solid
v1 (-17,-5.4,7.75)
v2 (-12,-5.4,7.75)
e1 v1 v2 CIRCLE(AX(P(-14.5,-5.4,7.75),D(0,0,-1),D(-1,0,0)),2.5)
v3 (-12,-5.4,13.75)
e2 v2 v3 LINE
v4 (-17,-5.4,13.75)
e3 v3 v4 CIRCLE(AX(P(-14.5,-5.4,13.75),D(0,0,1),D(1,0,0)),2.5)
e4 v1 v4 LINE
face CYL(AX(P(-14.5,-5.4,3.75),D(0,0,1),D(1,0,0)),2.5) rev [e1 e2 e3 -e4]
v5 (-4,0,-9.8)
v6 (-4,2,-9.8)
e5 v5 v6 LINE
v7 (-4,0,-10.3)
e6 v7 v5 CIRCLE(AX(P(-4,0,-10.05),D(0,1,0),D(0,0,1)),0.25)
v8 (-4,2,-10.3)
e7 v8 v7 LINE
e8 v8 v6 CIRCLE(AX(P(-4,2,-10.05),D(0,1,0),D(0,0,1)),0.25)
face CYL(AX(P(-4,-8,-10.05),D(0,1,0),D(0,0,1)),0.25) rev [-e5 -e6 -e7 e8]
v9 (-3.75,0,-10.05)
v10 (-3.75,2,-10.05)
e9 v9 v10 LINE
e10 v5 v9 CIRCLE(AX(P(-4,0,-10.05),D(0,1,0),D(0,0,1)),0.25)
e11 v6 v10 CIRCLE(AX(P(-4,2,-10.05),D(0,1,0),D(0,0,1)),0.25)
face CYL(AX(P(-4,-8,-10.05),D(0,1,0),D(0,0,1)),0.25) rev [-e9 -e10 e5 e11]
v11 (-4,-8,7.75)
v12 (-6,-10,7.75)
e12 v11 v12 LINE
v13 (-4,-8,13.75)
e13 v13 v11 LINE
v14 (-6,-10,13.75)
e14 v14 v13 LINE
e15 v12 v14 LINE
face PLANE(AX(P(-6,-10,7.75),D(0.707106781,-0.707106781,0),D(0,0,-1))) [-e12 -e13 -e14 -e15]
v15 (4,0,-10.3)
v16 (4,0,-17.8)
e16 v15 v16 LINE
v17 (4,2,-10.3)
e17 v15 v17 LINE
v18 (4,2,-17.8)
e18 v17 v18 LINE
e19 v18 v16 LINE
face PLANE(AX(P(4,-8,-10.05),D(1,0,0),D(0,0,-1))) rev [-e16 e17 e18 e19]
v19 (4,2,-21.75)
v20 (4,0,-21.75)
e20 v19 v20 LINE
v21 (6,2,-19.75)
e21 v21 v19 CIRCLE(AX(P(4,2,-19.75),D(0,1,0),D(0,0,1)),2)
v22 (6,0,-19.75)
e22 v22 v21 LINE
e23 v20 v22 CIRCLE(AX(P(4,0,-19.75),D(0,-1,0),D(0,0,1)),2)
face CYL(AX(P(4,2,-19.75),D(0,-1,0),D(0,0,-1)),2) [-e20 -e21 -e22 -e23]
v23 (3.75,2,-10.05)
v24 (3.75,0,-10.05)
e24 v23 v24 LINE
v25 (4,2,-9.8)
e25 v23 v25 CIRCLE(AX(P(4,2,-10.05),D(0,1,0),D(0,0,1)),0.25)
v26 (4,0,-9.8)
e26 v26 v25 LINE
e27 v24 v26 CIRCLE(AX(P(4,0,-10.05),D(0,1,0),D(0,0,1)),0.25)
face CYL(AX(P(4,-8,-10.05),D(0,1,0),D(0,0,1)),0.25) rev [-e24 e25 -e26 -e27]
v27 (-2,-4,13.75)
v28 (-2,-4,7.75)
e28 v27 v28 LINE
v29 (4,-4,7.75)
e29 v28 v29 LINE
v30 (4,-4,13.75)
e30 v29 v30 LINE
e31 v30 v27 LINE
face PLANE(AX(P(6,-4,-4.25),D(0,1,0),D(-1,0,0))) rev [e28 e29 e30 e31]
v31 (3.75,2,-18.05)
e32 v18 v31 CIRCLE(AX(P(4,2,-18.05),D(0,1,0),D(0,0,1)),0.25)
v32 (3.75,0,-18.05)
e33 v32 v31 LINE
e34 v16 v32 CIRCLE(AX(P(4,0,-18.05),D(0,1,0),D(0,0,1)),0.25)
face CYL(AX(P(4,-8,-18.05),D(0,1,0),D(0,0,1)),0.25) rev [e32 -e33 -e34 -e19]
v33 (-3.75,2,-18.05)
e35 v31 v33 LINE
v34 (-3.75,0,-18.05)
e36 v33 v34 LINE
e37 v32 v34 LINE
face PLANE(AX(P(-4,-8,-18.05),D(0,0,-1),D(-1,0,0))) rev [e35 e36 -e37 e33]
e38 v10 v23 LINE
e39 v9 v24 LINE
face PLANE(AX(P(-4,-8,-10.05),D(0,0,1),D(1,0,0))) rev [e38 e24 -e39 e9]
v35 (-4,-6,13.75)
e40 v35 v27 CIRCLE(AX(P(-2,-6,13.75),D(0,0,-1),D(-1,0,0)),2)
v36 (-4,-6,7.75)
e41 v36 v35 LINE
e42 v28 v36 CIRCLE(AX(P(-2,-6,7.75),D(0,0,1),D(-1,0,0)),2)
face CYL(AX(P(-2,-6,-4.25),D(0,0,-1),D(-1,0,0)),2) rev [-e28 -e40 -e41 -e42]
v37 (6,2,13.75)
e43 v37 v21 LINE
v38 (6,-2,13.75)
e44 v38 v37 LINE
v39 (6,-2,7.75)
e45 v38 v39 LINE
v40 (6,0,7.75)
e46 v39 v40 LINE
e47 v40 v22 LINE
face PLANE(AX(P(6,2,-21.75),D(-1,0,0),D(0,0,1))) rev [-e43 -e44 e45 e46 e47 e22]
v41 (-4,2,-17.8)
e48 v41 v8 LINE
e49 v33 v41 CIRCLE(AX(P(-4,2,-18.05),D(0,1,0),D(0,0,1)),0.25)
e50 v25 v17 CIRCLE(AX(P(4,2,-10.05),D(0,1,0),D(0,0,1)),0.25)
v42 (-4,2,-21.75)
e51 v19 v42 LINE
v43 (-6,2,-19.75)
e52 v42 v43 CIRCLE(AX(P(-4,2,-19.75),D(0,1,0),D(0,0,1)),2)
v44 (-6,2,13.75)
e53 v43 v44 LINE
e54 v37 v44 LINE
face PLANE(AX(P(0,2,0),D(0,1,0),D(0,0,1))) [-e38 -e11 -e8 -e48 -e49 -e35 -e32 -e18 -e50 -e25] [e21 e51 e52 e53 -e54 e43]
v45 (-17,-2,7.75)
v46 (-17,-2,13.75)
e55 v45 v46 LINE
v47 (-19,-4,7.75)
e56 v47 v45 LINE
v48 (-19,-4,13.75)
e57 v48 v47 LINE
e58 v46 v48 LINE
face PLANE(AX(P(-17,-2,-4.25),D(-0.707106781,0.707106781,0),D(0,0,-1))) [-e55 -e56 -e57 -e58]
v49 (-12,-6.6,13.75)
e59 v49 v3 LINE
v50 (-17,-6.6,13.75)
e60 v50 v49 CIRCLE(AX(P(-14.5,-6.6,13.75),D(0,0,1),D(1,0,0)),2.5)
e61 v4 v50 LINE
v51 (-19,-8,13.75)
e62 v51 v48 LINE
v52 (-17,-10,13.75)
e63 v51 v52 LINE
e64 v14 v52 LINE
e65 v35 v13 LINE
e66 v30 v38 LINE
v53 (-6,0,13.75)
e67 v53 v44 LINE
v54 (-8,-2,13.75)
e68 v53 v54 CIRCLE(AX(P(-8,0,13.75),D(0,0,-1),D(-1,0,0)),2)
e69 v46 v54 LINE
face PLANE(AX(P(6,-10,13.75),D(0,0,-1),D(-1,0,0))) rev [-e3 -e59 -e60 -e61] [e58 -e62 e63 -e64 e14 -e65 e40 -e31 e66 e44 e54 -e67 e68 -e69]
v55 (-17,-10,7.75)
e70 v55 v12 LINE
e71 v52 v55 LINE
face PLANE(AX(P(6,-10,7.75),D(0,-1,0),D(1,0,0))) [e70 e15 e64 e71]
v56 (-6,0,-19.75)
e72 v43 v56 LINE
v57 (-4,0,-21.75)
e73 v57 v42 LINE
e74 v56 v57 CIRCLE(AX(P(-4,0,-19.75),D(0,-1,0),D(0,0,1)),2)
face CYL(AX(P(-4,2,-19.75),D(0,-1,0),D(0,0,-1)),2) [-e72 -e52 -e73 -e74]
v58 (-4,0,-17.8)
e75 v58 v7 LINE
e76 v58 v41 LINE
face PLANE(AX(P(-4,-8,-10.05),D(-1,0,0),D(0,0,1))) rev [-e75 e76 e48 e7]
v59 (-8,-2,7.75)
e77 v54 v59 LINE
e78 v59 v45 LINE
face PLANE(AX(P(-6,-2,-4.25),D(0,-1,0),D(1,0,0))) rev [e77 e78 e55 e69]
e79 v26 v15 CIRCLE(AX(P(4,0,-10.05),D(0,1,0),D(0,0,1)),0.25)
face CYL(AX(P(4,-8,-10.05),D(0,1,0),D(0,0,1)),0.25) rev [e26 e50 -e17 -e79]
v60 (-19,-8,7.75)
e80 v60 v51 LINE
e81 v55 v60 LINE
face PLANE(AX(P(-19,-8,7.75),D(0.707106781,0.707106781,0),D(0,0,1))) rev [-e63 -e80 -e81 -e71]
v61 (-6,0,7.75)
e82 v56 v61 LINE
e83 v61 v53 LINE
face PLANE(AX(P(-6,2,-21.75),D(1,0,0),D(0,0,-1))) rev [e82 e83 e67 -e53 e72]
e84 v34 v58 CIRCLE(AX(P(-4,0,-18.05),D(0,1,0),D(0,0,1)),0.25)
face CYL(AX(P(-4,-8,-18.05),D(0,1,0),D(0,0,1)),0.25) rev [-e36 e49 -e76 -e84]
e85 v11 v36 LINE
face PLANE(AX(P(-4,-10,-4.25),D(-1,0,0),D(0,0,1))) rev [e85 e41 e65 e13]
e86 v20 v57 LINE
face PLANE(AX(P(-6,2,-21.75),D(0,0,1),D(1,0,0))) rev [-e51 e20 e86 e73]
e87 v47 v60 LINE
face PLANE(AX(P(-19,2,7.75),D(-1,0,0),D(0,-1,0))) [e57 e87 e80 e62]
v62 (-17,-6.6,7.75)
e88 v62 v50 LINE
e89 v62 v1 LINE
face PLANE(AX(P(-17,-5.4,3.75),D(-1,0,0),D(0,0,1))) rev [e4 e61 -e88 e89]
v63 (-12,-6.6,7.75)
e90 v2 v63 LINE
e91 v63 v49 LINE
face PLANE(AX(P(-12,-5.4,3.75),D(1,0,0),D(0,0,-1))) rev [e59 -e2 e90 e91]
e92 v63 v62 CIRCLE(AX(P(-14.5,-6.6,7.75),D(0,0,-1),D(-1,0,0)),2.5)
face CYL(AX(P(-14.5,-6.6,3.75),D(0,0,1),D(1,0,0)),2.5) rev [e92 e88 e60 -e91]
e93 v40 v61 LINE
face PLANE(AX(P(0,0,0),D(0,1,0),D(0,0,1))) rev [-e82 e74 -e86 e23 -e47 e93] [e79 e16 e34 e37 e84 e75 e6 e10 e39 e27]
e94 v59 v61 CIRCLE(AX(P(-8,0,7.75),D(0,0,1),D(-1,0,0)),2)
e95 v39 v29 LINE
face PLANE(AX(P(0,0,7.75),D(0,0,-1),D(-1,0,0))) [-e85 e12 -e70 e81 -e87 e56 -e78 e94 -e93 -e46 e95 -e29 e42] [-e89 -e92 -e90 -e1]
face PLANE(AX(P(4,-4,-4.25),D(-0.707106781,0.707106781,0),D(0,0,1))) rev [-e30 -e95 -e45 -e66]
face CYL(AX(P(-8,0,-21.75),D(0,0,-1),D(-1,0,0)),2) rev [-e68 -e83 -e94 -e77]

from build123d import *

# Parameters (mm, degrees)
SKETCH1_W             = 12
SKETCH1_H             = 43.5
BOSS_EXTRUDE1_DEPTH   = 2
M3_TAPPED_HOLE1_D     = 2.5
M3_TAPPED_HOLE1_DEPTH = 7.5
M3_TAPPED_HOLE1_TIP   = 0.751075774
SKETCH6_W             = 25
SKETCH6_H             = 12
BOSS_EXTRUDE2_DEPTH   = 14
SKETCH7_W             = 25
SKETCH7_H             = 8
CUT_EXTRUDE4_DEPTH    = 32.273990791
SKETCH8_R             = 2.5
CUT_EXTRUDE5_DEPTH    = 15
SKETCH9_W             = 13
SKETCH9_H             = 4
SKETCH9_W_2           = 10
SKETCH9_H_2           = 6
CUT_EXTRUDE6_DEPTH    = 18
CHAMFER2_SIZE         = 2
FILLET1_R             = 2
FILLET2_R             = 2
SKETCH3_W             = 8
SKETCH3_H             = 8
CUT_EXTRUDE2_DEPTH    = 10
SKETCH10_R            = 0.25
CUT_EXTRUDE7_DEPTH    = 10
CUT_EXTRUDE8_DEPTH    = 10


with BuildPart() as part:
    # Sketch1 → Boss-Extrude1 (new body)
    with BuildSketch(Plane(origin=(0, 0, 0), x_dir=(1, 0, 0), z_dir=(0, 1, 0))):
        Rectangle(SKETCH1_W, SKETCH1_H)
    extrude(amount=BOSS_EXTRUDE1_DEPTH)

    # M3 Tapped Hole1
    with Locations(Plane(origin=(0, 2, 17.75), x_dir=(0, 0, 1), z_dir=(0, 1, 0))):
        with Locations((0, 0)):
            Hole(M3_TAPPED_HOLE1_D / 2, depth=M3_TAPPED_HOLE1_DEPTH)
            with Locations((0, 0, -(M3_TAPPED_HOLE1_DEPTH + M3_TAPPED_HOLE1_TIP / 2))):  # 118° drill point
                Cone(0, M3_TAPPED_HOLE1_D / 2, M3_TAPPED_HOLE1_TIP, mode=Mode.SUBTRACT)

    # Sketch6 → Boss-Extrude2 (add)
    with BuildSketch(Plane.XY.offset(21.75)):
        with Locations((-6.5, -4)):
            Rectangle(SKETCH6_W, SKETCH6_H)
    extrude(amount=-BOSS_EXTRUDE2_DEPTH)

    # Sketch7 → Cut-Extrude4 (cut, through all)
    with BuildSketch(Plane(origin=(0, 2, 0), x_dir=(1, 0, 0), z_dir=(0, 1, 0))):
        with Locations((-6.5, -17.75)):
            Rectangle(SKETCH7_W, SKETCH7_H)
    extrude(amount=-CUT_EXTRUDE4_DEPTH, mode=Mode.SUBTRACT)

    # Sketch8 → Cut-Extrude5 (cut)
    with BuildSketch(Plane.XY.offset(13.75)):
        with Locations((-14.5, -6)):
            Circle(SKETCH8_R)
    extrude(amount=-CUT_EXTRUDE5_DEPTH, mode=Mode.SUBTRACT)

    # Sketch9 → Cut-Extrude6 (cut)
    with BuildSketch(Plane.XY.offset(13.75)):
        with Locations((-12.5, 0)):
            Rectangle(SKETCH9_W, SKETCH9_H)
        with Locations((1, -7)):
            Rectangle(SKETCH9_W_2, SKETCH9_H_2)
    extrude(amount=-CUT_EXTRUDE6_DEPTH, mode=Mode.SUBTRACT)

    # Chamfer2
    chamfer2_edges = [part.edges().sort_by_distance(p)[0] for p in [
        (-19, -10, 10.75),
        (-19, -2, 10.75),
        (6, -4, 10.75),
        (-4, -10, 10.75),
    ]]
    chamfer(chamfer2_edges, length=CHAMFER2_SIZE)

    # Fillet1
    fillet1_edges = [part.edges().sort_by_distance(p)[0] for p in [
        (-4, -4, 10.75),
        (-6, -2, 10.75),
    ]]
    fillet(fillet1_edges, radius=FILLET1_R)

    # Fillet2
    fillet2_edges = [part.edges().sort_by_distance(p)[0] for p in [
        (-6, 1, -21.75),
        (6, 1, -21.75),
    ]]
    fillet(fillet2_edges, radius=FILLET2_R)

    # Sketch3 → Cut-Extrude2 (cut)
    with BuildSketch(Plane(origin=(0, 2, 0), x_dir=(1, 0, 0), z_dir=(0, 1, 0))):
        with Locations((0, 14.05)):
            Rectangle(SKETCH3_W, SKETCH3_H)
    extrude(amount=-CUT_EXTRUDE2_DEPTH, mode=Mode.SUBTRACT)

    # Sketch10 → Cut-Extrude7 (cut)
    with BuildSketch(Plane(origin=(0, 2, 0), x_dir=(1, 0, 0), z_dir=(0, 1, 0))):
        with Locations((-4, 10.05)):
            Circle(SKETCH10_R)
        with Locations((4, 10.05)):
            Circle(SKETCH10_R)
        with Locations((-4, 18.05)):
            Circle(SKETCH10_R)
        with Locations((4, 18.05)):
            Circle(SKETCH10_R)
    extrude(amount=-CUT_EXTRUDE7_DEPTH, mode=Mode.SUBTRACT)

    # Sketch11 → Cut-Extrude8 (cut)
    with BuildSketch(Plane.XY.offset(13.75)):
        with BuildLine():
            Line((-12, -5.4), (-12, -6.6))
            ThreePointArc((-12, -6.6), (-14.5, -9.1), (-17, -6.6))
            Line((-17, -6.6), (-17, -5.4))
            ThreePointArc((-17, -5.4), (-14.5, -2.9), (-12, -5.4))
        make_face()
    extrude(amount=-CUT_EXTRUDE8_DEPTH, mode=Mode.SUBTRACT)


solid = part.part
